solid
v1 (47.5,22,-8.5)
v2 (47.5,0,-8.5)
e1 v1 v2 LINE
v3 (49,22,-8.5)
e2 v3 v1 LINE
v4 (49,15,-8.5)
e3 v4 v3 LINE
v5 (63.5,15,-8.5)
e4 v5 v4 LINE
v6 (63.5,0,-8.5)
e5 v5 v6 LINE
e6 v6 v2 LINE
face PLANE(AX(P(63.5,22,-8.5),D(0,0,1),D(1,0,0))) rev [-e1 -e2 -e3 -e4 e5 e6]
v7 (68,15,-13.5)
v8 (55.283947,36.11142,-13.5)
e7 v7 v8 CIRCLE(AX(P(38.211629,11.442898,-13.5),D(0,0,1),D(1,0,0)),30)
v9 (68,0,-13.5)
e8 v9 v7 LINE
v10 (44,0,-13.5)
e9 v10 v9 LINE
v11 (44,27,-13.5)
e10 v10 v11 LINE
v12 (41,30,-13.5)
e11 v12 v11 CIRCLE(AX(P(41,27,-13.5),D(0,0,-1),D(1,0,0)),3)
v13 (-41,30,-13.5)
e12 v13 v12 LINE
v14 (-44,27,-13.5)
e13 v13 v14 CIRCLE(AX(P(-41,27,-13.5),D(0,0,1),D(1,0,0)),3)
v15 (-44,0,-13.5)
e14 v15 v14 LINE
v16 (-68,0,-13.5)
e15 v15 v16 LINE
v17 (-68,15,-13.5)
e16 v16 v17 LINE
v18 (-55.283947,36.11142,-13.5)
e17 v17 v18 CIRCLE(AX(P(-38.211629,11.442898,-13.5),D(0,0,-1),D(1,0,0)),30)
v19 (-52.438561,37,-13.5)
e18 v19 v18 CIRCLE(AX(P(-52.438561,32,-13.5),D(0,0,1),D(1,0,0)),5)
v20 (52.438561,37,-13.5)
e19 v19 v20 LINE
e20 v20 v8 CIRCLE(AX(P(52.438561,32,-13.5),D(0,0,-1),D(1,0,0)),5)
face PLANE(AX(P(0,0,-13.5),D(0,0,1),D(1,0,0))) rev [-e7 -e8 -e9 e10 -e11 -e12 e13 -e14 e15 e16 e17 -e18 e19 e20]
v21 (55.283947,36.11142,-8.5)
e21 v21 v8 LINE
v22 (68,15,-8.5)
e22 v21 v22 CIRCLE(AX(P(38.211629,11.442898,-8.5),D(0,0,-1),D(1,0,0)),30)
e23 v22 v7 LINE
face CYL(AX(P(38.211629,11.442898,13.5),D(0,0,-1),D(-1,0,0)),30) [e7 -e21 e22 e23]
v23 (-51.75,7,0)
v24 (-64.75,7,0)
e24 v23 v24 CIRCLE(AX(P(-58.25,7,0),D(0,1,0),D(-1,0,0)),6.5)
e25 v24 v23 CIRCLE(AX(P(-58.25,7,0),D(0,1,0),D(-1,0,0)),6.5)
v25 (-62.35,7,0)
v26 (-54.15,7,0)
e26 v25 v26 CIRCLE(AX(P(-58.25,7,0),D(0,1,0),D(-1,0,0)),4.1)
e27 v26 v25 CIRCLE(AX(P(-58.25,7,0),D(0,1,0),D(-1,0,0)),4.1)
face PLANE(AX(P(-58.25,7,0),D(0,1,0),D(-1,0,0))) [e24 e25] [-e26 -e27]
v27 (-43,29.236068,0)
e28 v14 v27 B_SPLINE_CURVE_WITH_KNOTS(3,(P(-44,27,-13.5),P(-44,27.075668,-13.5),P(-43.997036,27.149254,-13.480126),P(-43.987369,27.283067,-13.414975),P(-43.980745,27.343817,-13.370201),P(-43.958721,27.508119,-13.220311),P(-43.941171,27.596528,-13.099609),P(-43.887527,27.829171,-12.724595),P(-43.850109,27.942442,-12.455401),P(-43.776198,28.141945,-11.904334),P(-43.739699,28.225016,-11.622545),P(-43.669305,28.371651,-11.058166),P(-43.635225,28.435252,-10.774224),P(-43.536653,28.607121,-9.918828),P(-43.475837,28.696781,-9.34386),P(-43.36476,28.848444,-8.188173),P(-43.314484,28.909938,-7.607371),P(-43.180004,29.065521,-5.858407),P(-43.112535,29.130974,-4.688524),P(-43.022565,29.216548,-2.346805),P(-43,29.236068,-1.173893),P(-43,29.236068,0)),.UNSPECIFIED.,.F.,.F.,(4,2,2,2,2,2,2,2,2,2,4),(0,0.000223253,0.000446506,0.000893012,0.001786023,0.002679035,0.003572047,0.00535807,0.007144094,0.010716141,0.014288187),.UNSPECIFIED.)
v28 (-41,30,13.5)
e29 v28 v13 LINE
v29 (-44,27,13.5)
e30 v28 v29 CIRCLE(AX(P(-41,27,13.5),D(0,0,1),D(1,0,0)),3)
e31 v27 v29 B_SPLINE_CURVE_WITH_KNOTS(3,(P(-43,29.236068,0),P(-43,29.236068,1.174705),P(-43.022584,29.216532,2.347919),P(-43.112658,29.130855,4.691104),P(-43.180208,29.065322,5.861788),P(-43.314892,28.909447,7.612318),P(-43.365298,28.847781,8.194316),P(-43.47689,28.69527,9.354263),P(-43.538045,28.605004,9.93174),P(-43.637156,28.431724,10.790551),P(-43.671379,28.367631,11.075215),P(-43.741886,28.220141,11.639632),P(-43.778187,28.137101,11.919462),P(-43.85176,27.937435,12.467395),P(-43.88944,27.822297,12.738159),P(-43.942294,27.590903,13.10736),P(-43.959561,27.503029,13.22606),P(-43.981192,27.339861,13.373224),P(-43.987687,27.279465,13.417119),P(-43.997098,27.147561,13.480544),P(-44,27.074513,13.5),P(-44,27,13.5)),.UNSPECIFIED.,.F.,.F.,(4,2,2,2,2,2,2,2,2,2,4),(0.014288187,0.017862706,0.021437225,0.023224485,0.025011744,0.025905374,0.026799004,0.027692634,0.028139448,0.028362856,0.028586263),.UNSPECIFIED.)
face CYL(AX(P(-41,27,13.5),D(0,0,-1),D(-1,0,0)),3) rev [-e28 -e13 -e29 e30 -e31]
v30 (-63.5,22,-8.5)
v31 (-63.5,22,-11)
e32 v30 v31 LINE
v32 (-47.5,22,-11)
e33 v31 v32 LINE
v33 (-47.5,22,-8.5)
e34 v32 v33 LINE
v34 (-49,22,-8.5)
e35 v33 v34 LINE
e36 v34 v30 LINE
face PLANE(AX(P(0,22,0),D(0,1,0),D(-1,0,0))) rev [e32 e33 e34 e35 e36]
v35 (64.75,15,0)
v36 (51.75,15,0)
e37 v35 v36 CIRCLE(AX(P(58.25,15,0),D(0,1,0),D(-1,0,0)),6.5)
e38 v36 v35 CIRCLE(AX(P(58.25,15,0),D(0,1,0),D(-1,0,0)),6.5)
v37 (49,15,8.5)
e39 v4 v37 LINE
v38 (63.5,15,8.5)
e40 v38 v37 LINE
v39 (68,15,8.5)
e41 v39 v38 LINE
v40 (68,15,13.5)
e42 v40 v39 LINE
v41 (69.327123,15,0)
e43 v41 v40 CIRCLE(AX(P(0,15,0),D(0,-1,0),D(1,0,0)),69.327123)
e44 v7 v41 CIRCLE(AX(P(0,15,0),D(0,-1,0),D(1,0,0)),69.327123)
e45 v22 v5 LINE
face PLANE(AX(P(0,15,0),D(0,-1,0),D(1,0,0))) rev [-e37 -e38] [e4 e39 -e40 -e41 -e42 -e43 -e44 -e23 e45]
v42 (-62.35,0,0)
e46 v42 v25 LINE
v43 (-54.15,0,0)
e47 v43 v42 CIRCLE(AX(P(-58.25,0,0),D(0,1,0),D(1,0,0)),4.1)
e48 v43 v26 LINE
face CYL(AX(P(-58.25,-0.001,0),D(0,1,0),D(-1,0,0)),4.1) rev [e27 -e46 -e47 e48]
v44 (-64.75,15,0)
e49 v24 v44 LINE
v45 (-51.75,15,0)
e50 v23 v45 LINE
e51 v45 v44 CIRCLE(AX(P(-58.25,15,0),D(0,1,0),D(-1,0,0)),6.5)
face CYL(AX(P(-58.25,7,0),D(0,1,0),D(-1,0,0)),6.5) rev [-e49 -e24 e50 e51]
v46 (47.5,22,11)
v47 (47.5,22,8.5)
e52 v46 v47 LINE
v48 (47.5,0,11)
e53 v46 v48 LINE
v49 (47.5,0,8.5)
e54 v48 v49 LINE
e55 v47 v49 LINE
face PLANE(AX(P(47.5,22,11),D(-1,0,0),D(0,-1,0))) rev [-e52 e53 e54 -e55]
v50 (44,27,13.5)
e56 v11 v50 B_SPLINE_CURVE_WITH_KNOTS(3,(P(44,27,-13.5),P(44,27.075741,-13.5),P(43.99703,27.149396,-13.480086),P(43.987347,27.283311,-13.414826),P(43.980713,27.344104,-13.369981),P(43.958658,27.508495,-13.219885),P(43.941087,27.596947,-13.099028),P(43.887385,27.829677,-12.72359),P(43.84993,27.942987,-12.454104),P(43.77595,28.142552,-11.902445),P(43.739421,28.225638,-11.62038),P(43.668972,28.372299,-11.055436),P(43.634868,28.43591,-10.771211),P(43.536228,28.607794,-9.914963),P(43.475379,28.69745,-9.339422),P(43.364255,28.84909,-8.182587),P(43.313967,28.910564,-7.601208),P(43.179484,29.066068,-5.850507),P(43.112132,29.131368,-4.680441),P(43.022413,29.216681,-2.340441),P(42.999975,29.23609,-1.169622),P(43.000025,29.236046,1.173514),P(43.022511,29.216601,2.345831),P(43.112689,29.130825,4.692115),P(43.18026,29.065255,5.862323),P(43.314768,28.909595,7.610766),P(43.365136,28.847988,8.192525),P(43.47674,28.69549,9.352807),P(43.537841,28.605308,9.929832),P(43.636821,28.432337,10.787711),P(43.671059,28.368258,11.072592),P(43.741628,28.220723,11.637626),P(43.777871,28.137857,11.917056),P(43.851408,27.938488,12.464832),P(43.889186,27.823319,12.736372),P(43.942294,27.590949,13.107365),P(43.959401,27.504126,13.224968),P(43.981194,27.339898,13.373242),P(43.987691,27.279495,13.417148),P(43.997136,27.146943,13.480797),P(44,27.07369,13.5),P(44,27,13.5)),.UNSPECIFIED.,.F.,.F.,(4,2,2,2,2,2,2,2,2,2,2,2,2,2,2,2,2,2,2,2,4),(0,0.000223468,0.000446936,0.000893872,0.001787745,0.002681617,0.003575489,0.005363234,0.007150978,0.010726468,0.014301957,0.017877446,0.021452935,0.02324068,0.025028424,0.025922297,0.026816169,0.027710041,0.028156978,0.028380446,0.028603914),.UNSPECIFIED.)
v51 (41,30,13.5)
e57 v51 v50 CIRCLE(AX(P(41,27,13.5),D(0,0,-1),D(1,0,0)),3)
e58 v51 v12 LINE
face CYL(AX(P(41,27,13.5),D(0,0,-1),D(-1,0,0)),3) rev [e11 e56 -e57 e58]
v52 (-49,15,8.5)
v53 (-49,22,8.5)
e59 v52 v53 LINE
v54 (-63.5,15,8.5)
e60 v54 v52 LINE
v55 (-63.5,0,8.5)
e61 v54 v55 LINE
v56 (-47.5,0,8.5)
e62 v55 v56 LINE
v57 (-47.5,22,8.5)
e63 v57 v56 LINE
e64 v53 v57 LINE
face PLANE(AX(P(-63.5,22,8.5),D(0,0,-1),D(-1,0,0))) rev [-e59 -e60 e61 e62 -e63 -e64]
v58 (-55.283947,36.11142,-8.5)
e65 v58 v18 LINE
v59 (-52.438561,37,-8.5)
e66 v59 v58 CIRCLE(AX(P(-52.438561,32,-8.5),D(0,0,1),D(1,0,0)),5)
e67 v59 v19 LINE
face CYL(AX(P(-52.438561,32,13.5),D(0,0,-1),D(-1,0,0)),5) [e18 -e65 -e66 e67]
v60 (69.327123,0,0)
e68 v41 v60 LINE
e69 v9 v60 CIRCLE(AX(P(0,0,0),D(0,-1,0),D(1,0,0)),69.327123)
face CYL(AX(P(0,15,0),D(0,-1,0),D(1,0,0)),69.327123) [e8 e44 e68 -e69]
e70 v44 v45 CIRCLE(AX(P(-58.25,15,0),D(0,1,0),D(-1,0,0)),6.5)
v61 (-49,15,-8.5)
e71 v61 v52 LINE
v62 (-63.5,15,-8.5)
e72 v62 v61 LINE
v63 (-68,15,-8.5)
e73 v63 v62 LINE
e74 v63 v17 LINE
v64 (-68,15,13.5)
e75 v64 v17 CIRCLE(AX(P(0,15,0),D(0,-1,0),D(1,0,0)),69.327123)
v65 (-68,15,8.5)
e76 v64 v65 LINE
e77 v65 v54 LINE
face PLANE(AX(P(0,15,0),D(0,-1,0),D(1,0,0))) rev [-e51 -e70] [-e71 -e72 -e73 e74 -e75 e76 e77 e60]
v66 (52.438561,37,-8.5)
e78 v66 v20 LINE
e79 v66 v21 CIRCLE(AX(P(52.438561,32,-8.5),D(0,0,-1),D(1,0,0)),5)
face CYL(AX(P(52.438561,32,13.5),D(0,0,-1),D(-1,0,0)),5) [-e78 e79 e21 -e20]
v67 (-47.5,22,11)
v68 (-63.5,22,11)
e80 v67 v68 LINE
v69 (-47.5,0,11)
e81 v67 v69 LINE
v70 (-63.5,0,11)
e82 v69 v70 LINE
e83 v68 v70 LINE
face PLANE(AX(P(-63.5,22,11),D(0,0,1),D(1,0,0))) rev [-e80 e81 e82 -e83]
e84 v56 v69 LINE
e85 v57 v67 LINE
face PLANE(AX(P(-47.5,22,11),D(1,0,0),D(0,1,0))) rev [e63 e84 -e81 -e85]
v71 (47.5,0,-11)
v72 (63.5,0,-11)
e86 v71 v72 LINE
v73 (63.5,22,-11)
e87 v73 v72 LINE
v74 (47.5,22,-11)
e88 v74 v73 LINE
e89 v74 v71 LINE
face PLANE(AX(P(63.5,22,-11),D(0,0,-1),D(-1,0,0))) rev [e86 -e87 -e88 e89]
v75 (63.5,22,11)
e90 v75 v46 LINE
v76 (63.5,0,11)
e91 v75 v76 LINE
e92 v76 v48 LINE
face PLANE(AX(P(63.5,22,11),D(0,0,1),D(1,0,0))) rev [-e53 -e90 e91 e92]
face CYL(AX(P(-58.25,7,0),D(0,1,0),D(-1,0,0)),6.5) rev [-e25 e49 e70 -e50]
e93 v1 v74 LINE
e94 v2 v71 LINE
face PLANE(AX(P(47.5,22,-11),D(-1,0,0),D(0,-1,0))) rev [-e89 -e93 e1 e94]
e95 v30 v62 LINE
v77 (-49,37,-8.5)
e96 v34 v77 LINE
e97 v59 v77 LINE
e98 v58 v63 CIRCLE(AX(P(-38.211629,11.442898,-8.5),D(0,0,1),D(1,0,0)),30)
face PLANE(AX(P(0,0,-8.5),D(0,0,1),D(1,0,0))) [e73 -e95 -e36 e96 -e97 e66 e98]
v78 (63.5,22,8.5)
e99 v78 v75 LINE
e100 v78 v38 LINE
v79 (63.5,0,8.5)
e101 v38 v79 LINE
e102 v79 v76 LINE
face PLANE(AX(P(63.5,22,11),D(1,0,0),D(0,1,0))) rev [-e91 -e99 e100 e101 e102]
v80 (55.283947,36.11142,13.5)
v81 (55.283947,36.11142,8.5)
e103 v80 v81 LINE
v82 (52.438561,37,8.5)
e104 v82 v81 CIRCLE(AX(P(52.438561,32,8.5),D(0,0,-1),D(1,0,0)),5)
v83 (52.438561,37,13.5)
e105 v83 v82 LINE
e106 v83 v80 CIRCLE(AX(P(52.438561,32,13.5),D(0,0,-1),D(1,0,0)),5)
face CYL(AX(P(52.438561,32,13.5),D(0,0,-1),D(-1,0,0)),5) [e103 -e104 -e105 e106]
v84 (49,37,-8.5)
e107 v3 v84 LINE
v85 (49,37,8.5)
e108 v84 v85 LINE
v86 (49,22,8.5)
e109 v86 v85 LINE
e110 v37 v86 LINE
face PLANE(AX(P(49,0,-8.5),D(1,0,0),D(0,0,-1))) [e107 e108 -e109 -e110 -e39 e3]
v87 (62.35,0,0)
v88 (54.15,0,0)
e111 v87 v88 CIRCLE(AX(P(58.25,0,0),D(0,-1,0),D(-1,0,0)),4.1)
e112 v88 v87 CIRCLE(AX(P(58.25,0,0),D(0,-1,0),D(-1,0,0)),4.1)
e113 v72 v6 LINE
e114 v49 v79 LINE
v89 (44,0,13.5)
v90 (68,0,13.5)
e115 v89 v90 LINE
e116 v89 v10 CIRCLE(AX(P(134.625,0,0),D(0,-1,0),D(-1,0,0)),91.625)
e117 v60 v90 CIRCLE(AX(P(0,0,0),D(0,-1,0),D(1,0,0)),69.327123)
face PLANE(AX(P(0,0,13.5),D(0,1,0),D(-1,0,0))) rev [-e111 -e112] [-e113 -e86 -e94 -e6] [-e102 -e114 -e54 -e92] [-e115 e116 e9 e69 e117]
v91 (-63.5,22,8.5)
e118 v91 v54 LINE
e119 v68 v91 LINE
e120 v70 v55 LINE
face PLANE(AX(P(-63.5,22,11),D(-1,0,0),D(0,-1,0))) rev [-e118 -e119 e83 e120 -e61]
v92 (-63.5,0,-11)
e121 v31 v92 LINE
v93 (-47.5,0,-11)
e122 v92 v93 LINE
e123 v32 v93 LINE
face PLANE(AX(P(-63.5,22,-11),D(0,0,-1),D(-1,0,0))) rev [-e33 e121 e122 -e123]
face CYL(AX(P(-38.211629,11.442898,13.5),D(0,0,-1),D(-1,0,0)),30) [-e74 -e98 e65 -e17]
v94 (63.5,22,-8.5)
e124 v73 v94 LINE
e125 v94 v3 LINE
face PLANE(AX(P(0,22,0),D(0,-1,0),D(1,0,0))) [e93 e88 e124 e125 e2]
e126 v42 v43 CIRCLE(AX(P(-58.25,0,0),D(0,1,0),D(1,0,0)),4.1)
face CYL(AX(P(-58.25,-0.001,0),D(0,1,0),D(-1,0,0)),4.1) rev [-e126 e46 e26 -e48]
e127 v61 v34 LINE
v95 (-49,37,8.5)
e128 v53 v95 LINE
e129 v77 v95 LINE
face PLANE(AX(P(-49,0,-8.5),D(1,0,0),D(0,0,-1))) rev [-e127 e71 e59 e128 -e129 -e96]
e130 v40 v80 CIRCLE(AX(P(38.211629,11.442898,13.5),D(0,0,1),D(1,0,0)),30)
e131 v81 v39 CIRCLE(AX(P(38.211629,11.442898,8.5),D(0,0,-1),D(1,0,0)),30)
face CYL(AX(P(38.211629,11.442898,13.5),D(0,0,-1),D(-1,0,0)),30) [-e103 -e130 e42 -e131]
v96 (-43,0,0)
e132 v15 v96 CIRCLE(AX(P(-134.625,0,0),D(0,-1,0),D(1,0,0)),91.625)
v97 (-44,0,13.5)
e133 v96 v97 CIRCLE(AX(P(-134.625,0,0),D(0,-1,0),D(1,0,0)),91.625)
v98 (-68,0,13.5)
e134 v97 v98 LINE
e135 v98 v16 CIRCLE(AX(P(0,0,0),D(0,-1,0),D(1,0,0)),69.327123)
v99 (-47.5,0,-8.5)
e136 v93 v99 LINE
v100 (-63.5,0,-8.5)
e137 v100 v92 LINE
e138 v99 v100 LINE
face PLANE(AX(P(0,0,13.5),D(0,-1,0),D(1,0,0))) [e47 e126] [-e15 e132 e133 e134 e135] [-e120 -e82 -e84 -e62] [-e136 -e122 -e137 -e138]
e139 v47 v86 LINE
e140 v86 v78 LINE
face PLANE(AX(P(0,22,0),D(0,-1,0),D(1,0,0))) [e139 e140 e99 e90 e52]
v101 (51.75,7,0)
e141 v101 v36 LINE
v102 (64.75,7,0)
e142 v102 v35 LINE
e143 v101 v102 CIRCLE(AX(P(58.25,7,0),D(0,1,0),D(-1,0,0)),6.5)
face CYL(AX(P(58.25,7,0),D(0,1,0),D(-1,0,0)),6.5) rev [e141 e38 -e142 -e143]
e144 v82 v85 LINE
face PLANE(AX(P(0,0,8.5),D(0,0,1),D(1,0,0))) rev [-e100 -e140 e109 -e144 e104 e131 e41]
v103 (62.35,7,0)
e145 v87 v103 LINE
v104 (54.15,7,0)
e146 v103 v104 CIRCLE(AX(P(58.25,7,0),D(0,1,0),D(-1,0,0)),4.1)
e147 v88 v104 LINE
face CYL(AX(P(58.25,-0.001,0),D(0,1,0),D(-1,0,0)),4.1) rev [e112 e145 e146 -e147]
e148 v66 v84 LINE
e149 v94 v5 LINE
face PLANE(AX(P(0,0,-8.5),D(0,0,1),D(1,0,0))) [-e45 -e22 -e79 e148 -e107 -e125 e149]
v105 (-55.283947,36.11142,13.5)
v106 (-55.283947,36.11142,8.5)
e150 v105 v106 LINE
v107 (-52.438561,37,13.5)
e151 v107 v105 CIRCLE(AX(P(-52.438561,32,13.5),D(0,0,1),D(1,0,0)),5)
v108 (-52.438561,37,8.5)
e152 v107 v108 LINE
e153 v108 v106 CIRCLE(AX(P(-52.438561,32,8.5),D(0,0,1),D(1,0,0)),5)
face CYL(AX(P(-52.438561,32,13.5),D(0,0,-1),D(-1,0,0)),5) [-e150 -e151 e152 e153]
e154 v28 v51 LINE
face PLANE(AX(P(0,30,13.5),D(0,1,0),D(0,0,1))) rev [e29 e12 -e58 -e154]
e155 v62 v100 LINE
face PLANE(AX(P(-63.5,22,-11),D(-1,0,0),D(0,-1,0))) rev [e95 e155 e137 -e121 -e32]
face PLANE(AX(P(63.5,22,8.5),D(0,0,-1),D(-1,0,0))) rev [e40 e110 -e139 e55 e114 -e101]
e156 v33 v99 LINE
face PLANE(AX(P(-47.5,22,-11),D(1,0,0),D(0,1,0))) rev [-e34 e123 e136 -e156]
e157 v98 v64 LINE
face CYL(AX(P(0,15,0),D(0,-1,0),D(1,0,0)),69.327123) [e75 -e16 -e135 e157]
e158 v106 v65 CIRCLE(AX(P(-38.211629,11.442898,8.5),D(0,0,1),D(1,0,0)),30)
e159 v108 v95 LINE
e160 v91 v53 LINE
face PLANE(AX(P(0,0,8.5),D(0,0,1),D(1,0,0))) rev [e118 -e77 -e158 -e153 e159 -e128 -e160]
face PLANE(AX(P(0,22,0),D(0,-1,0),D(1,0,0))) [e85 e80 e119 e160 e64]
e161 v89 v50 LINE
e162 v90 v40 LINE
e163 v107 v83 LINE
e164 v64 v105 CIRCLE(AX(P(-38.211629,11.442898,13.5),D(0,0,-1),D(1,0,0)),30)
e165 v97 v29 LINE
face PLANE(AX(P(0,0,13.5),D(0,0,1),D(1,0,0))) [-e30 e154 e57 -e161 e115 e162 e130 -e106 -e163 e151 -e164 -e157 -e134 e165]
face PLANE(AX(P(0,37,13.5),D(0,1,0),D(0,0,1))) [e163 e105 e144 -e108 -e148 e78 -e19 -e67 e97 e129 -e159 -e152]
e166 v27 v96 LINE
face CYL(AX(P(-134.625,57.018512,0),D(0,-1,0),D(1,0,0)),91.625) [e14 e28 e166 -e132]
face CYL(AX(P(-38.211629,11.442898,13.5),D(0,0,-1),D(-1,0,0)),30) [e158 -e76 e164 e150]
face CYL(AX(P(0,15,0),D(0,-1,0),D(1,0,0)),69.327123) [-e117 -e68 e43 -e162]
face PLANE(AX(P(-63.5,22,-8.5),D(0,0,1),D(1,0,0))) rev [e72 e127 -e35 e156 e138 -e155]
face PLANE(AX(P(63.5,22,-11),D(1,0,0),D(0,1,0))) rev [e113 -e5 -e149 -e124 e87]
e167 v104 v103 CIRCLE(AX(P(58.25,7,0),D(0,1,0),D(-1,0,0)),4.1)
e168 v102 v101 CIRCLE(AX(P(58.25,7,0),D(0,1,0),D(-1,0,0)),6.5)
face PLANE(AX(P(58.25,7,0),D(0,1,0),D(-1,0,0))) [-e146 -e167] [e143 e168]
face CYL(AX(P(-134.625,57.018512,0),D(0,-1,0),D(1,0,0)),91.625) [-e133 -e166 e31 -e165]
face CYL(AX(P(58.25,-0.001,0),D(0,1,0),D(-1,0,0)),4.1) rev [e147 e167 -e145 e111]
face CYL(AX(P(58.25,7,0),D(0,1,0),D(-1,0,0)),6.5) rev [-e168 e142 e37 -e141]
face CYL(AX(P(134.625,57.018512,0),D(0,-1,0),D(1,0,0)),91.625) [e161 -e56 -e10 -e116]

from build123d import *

# Parameters (mm, degrees)
EXTRUDE_1_DEPTH     = 13.5
EXTRUDE_2_REACH     = 80.583
EXTRUDE_3_DEPTH     = 15
CUT_EXTRUDE_1_DEPTH = 8.5
SKETCH_6_W          = 16
SKETCH_6_H          = 2.5
CUT_EXTRUDE_2_DEPTH = 22
SKETCH_7_R          = 6.5
CUT_EXTRUDE_3_DEPTH = 8
CUT_EXTRUDE_4_REACH = 78.737
SKETCH_8_R          = 4.1


with BuildPart() as part:
    # 草图1 → 凸台-拉伸1 (new, symmetric)
    with BuildSketch(Plane.XY):
        with BuildLine():
            Line((68, 0), (68, 15))
            ThreePointArc((68, 15), (63.909956901, 26.921785896), (55.283946786, 36.111420329))
            ThreePointArc((55.283946786, 36.111420329), (53.929013217, 36.772688008), (52.438560542, 37))
            Line((52.438560542, 37), (-52.438560542, 37))
            ThreePointArc((-52.438560542, 37), (-53.929013217, 36.772688008), (-55.283946786, 36.111420329))
            ThreePointArc((-55.283946786, 36.111420329), (-63.909956901, 26.921785896), (-68, 15))
            Line((-68, 15), (-68, 0))
            Line((-68, 0), (-44, 0))
            Line((-44, 0), (-44, 27))
            ThreePointArc((-44, 27), (-43.121320344, 29.121320344), (-41, 30))
            Line((-41, 30), (41, 30))
            ThreePointArc((41, 30), (43.121320344, 29.121320344), (44, 27))
            Line((44, 27), (44, 0))
            Line((44, 0), (68, 0))
        make_face()
    extrude(amount=EXTRUDE_1_DEPTH, both=True)

    # 凸台-拉伸2: up to this face of the body (flat: up to its plane)
    extrude_2_end = Plane(part.part.faces().sort_by_distance((0, 30, 0))[0])
    # 草图2 → 凸台-拉伸2 (add, up to the picked face)
    with BuildSketch(Plane.XZ, mode=Mode.PRIVATE) as extrude_2_sk1:
        with BuildLine():
            Line((-44, 13.5), (-44, -13.5))
            ThreePointArc((-44, -13.5), (-43, 0), (-44, 13.5))
        make_face()
    extrude_2_tool1 = split(extrude(extrude_2_sk1.sketch, amount=-EXTRUDE_2_REACH, mode=Mode.PRIVATE), bisect_by=extrude_2_end, keep=Keep.BOTH, mode=Mode.PRIVATE)
    # 草图2 → 凸台-拉伸2 (add, up to the picked face)
    with BuildSketch(Plane.XZ, mode=Mode.PRIVATE) as extrude_2_sk2:
        with BuildLine():
            Line((44, 13.5), (44, -13.5))
            ThreePointArc((44, -13.5), (43, 0), (44, 13.5))
        make_face()
    extrude_2_tool2 = split(extrude(extrude_2_sk2.sketch, amount=-EXTRUDE_2_REACH, mode=Mode.PRIVATE), bisect_by=extrude_2_end, keep=Keep.BOTH, mode=Mode.PRIVATE)
    add(extrude_2_tool1.solids().sort_by(Axis((-43.599812, 0, 0), (0, 1, 0)))[0])
    add(extrude_2_tool2.solids().sort_by(Axis((43.599812, 0, 0), (0, 1, 0)))[0])

    # 草图4 → 凸台-拉伸3 (add)
    with BuildSketch(Plane.XZ):
        with BuildLine():
            Line((-68, 13.5), (-68, -13.5))
            ThreePointArc((-68, -13.5), (-69.327123119, 0), (-68, 13.5))
        make_face()
        with BuildLine():
            Line((68, 13.5), (68, -13.5))
            ThreePointArc((68, -13.5), (69.327123119, 0), (68, 13.5))
        make_face()
    extrude(amount=-EXTRUDE_3_DEPTH)

    # 草图5 → 切除-拉伸1 (cut, symmetric)
    with BuildSketch(Plane.XY):
        with BuildLine():
            ThreePointArc((-52.438560542, 37), (-53.929013217, 36.772688008), (-55.283946786, 36.111420329))
            ThreePointArc((-55.283946786, 36.111420329), (-63.909956901, 26.921785896), (-68, 15))
            Line((-68, 15), (-49, 15))
            Line((-49, 15), (-49, 37))
            Line((-49, 37), (-52.438560542, 37))
        make_face()
        with BuildLine():
            ThreePointArc((52.438560542, 37), (53.929013217, 36.772688008), (55.283946786, 36.111420329))
            ThreePointArc((55.283946786, 36.111420329), (63.909956901, 26.921785896), (68, 15))
            Line((68, 15), (49, 15))
            Line((49, 15), (49, 37))
            Line((49, 37), (52.438560542, 37))
        make_face()
    extrude(amount=CUT_EXTRUDE_1_DEPTH, both=True, mode=Mode.SUBTRACT)

    # 草图6 → 切除-拉伸2 (cut)
    with BuildSketch(Plane.XZ):
        with Locations((-55.5, 9.75)):
            Rectangle(SKETCH_6_W, SKETCH_6_H)
        with Locations((55.5, 9.75)):
            Rectangle(SKETCH_6_W, SKETCH_6_H)
        with Locations((55.5, -9.75)):
            Rectangle(SKETCH_6_W, SKETCH_6_H)
        with Locations((-55.5, -9.75)):
            Rectangle(SKETCH_6_W, SKETCH_6_H)
    extrude(amount=-CUT_EXTRUDE_2_DEPTH, mode=Mode.SUBTRACT)

    # 草图7 → 切除-拉伸3 (cut)
    with BuildSketch(Plane(origin=(0, 15, 0), x_dir=(1, 0, 0), z_dir=(0, 1, 0))):
        with Locations(Location((-58.25, 0, 0), (0, 0, 180))):
            Circle(SKETCH_7_R)
        with Locations(Location((58.25, 0, 0), (0, 0, 180))):
            Circle(SKETCH_7_R)
    extrude(amount=-CUT_EXTRUDE_3_DEPTH, mode=Mode.SUBTRACT)

    # 草图8 → 切除-拉伸4 (cut, up to next)
    with BuildSketch(Plane(origin=(0, 7, 0), x_dir=(1, 0, 0), z_dir=(0, 1, 0)), mode=Mode.PRIVATE) as cut_extrude_4_sk1:
        with Locations(Location((58.25, 0, 0), (0, 0, 180))):
            Circle(SKETCH_8_R)
    cut_extrude_4_tool1 = extrude(cut_extrude_4_sk1.sketch, amount=-CUT_EXTRUDE_4_REACH, mode=Mode.PRIVATE) & part.part
    # 草图8 → 切除-拉伸4 (cut, up to next)
    with BuildSketch(Plane(origin=(0, 7, 0), x_dir=(1, 0, 0), z_dir=(0, 1, 0)), mode=Mode.PRIVATE) as cut_extrude_4_sk2:
        with Locations(Location((-58.25, 0, 0), (0, 0, 180))):
            Circle(SKETCH_8_R)
    cut_extrude_4_tool2 = extrude(cut_extrude_4_sk2.sketch, amount=-CUT_EXTRUDE_4_REACH, mode=Mode.PRIVATE) & part.part
    add(cut_extrude_4_tool1.solids().sort_by_distance((58.25, 7, 0))[0], mode=Mode.SUBTRACT)
    add(cut_extrude_4_tool2.solids().sort_by_distance((-58.25, 7, 0))[0], mode=Mode.SUBTRACT)


solid = part.part
